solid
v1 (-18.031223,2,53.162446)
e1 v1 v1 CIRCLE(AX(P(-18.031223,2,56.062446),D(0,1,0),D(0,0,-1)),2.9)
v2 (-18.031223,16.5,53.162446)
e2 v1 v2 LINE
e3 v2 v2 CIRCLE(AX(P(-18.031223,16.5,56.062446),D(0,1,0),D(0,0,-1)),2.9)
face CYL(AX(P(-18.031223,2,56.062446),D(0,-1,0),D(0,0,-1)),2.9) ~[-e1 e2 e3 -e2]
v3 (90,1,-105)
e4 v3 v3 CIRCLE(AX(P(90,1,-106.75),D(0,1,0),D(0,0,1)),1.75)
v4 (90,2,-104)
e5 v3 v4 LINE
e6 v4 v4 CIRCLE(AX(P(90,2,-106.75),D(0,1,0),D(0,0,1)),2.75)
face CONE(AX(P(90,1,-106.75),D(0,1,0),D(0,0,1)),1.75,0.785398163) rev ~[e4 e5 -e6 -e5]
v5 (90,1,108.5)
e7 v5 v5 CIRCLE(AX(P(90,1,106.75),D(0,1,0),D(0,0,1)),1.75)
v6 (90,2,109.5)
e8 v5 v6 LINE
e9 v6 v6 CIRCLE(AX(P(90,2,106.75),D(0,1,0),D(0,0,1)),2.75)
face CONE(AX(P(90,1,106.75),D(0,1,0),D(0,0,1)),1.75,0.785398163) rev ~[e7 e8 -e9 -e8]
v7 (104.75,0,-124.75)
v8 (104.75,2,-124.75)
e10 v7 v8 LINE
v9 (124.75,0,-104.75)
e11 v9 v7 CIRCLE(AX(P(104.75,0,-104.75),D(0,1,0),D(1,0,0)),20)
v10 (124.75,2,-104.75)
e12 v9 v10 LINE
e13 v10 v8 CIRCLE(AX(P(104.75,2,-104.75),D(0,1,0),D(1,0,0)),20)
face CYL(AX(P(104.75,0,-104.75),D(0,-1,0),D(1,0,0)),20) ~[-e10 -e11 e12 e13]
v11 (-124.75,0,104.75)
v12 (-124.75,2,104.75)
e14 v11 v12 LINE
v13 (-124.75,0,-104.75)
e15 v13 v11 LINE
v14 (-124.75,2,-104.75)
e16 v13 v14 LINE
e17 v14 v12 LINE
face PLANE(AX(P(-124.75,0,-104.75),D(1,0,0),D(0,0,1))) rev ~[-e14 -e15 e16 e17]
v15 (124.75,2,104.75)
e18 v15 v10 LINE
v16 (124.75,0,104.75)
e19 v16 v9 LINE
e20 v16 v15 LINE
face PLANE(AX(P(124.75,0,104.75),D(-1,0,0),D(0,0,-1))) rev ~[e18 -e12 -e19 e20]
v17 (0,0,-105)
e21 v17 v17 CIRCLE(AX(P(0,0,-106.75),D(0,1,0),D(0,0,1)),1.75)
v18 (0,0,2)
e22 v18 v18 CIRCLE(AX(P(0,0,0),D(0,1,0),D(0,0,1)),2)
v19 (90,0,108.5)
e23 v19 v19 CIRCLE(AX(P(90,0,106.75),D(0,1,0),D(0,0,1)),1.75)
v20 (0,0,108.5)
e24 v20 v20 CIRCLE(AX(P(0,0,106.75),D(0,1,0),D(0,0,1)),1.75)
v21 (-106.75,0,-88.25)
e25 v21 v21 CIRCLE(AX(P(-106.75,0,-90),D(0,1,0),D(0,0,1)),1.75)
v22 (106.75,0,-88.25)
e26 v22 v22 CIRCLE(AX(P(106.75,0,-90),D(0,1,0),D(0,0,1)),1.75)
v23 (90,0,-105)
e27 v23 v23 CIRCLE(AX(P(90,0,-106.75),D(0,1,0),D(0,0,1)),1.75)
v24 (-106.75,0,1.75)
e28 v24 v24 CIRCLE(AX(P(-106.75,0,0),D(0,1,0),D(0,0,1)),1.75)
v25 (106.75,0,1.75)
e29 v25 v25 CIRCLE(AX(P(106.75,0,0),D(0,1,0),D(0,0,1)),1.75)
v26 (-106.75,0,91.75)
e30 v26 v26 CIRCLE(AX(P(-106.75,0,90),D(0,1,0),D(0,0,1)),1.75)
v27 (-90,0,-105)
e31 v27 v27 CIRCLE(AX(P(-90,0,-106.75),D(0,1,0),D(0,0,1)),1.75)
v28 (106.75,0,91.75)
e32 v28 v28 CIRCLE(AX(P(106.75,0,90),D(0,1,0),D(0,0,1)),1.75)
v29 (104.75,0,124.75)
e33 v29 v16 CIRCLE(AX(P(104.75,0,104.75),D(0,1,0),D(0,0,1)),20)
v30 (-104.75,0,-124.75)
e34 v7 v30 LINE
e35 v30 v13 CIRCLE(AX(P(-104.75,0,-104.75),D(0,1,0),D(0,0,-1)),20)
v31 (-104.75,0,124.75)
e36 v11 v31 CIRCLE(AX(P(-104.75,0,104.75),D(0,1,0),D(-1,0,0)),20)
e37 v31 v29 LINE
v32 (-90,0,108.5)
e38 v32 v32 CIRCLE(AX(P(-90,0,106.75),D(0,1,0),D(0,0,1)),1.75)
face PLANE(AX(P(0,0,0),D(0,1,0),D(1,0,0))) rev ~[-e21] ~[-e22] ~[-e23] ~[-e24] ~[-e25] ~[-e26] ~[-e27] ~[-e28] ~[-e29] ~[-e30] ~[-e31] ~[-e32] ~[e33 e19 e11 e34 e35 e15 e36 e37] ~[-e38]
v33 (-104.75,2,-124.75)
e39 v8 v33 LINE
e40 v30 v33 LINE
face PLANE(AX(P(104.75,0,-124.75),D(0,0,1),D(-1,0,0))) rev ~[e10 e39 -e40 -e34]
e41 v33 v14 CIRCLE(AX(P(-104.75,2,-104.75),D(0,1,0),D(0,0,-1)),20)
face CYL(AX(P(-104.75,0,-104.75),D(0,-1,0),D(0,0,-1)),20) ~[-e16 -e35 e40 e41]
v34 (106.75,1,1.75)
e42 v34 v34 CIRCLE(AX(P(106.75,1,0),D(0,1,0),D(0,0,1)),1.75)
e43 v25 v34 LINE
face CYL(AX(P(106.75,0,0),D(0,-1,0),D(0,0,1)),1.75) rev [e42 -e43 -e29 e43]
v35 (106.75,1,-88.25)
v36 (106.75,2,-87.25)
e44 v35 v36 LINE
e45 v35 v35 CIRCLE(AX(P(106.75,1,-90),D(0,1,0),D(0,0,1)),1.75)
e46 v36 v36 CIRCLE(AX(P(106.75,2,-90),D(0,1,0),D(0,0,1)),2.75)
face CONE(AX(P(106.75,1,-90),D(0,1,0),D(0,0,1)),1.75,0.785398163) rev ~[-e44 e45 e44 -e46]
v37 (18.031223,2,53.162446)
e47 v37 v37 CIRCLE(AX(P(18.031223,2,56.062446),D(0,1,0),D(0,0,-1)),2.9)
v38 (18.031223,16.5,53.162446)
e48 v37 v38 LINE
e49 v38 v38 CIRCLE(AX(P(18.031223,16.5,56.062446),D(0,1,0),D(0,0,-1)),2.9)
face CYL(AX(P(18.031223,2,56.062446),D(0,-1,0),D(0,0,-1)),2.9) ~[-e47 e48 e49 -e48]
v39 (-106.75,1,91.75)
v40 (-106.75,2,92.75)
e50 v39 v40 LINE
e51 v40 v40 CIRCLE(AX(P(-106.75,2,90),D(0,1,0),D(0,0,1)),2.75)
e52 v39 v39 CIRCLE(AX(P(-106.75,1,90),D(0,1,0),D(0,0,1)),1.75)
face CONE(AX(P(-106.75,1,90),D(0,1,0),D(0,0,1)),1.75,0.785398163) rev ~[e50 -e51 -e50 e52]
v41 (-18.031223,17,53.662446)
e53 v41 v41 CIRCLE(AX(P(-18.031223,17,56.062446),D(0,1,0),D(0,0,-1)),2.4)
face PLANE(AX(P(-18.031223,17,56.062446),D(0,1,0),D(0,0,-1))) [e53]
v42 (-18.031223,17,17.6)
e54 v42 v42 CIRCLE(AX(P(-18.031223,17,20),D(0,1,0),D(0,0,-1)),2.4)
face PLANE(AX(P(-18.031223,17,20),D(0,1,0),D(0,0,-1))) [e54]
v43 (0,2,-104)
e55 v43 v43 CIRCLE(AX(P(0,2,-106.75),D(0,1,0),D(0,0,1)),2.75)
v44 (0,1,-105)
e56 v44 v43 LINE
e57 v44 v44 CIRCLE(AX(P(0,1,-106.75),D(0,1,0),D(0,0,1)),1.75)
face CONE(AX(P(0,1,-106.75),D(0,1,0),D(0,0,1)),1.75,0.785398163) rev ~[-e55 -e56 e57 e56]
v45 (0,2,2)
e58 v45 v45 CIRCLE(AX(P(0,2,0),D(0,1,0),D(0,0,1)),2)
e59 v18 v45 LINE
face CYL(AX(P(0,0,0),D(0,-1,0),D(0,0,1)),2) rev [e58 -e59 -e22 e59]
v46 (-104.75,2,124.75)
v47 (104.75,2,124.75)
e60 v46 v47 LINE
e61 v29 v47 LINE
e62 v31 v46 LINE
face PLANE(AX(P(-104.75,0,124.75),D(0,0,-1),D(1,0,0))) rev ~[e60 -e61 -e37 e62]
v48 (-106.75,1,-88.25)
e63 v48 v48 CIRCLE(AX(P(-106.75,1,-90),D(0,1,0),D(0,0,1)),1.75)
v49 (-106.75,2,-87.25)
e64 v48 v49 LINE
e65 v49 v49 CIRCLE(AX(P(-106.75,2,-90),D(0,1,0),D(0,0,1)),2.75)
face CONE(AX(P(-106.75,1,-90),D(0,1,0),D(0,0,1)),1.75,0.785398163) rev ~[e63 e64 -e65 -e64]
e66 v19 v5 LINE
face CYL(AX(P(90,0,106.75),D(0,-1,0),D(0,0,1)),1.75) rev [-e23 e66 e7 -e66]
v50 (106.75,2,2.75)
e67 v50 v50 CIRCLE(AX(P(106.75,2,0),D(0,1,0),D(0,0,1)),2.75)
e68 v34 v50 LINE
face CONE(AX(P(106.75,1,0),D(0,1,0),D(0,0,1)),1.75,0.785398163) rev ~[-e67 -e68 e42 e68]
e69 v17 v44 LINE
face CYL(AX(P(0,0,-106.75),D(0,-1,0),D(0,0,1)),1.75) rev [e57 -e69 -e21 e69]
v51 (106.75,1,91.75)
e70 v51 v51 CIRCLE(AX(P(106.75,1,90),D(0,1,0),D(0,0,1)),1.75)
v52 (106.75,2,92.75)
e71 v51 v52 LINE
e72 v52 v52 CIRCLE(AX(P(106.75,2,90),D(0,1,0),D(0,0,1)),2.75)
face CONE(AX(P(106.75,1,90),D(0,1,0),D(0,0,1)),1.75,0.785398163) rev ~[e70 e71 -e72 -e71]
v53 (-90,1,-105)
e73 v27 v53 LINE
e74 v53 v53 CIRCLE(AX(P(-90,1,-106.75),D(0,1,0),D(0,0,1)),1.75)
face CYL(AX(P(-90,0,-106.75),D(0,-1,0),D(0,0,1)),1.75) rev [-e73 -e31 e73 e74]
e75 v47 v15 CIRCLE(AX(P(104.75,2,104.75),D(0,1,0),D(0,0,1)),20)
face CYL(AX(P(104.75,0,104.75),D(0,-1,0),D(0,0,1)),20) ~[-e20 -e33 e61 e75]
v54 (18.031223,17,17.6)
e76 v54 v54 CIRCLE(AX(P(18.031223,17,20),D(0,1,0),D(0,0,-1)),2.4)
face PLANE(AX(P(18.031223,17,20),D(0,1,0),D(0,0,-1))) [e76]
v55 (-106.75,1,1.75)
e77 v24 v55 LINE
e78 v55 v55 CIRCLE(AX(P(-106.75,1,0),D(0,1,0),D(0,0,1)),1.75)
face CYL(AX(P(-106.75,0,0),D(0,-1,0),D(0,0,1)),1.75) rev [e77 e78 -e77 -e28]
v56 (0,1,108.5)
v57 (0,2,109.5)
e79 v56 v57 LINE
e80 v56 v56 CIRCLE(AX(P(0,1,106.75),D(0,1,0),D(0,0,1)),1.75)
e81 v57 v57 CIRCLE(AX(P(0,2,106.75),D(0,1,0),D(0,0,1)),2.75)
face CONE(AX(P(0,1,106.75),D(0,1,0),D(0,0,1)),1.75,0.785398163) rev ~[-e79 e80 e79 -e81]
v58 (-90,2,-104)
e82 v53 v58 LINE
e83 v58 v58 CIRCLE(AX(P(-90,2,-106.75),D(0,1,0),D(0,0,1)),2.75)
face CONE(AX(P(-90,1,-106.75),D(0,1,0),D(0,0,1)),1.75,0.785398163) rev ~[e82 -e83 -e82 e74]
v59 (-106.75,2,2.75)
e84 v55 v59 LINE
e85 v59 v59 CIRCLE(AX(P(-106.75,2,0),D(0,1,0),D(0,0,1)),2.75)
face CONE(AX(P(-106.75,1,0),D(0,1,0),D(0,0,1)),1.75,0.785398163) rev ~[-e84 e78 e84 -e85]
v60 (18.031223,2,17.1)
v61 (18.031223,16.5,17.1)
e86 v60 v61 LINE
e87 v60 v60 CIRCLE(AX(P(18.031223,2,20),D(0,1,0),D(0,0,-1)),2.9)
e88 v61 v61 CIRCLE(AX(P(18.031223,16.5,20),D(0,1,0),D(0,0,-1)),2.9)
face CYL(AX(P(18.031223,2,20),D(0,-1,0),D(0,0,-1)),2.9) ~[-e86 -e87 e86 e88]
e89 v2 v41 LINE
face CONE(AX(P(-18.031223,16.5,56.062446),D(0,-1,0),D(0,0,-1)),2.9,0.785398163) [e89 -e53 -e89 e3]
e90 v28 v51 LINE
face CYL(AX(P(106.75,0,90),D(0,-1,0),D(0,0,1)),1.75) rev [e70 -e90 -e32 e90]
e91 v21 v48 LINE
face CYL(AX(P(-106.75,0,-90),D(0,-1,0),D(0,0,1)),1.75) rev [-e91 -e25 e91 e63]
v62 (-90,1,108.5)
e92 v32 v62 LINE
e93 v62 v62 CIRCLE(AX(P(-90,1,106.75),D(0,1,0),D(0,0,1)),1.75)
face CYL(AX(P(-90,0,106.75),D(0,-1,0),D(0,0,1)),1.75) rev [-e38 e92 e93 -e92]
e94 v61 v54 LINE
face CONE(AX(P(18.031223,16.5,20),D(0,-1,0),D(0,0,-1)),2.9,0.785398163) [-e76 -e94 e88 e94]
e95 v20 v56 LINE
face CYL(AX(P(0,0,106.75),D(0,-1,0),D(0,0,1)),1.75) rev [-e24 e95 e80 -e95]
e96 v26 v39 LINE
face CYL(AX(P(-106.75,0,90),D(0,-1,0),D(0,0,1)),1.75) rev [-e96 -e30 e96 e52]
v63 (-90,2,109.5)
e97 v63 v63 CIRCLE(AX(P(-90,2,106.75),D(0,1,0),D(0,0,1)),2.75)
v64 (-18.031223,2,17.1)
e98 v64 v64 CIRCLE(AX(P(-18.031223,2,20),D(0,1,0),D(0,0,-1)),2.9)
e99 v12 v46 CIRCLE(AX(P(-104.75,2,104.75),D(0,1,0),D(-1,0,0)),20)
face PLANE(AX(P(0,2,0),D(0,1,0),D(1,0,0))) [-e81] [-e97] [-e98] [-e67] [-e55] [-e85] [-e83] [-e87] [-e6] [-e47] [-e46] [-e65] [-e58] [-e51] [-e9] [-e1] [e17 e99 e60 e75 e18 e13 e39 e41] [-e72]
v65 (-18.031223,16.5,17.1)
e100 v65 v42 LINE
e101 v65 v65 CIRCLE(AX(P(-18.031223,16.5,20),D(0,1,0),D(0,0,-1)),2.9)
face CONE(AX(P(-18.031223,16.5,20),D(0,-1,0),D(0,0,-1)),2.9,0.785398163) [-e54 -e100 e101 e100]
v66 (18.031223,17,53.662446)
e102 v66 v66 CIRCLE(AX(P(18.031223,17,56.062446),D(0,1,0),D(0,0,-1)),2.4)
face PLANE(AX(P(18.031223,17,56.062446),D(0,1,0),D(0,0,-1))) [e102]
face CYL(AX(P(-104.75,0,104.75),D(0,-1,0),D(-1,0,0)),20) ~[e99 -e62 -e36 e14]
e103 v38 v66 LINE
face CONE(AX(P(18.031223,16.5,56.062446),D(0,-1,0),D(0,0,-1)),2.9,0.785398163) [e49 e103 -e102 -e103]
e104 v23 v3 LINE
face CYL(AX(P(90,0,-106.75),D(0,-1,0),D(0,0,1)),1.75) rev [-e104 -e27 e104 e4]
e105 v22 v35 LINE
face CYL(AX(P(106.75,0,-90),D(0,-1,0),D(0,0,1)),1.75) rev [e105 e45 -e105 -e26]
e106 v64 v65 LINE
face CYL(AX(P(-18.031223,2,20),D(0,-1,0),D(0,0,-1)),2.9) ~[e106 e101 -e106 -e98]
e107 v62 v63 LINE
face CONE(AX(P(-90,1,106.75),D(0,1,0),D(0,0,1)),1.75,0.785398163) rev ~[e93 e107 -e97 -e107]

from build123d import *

# Parameters (mm, degrees)
SKETCH1_R           = 1.75
SKETCH1_R_2         = 2
BOSS_EXTRUDE1_DEPTH = 2
CHAMFER1_SIZE       = 1
SKETCH3_R           = 2.9
BOSS_EXTRUDE2_DEPTH = 15
CHAMFER2_SIZE       = 0.5


with BuildPart() as part:
    # Sketch1 → Boss-Extrude1 (new body)
    with BuildSketch(Plane(origin=(0, 0, 0), x_dir=(1, 0, 0), z_dir=(0, 1, 0))):
        with BuildLine():
            Line((-104.75, -124.75), (104.75, -124.75))
            ThreePointArc((104.75, -124.75), (118.892135624, -118.892135624), (124.75, -104.75))
            Line((124.75, -104.75), (124.75, 104.75))
            ThreePointArc((124.75, 104.75), (118.892135624, 118.892135624), (104.75, 124.75))
            Line((104.75, 124.75), (-104.75, 124.75))
            ThreePointArc((-104.75, 124.75), (-118.892135624, 118.892135624), (-124.75, 104.75))
            Line((-124.75, 104.75), (-124.75, -104.75))
            ThreePointArc((-124.75, -104.75), (-118.892135624, -118.892135624), (-104.75, -124.75))
        make_face()
        with Locations(Location((-90, 106.75, 0), (0, 0, 270))):
            Circle(SKETCH1_R, mode=Mode.SUBTRACT)
        with Locations(Location((0, 106.75, 0), (0, 0, 270))):
            Circle(SKETCH1_R, mode=Mode.SUBTRACT)
        with Locations(Location((90, 106.75, 0), (0, 0, 270))):
            Circle(SKETCH1_R, mode=Mode.SUBTRACT)
        with Locations(Location((106.75, 90, 0), (0, 0, 270))):
            Circle(SKETCH1_R, mode=Mode.SUBTRACT)
        with Locations(Location((106.75, 0, 0), (0, 0, 270))):
            Circle(SKETCH1_R, mode=Mode.SUBTRACT)
        with Locations(Location((106.75, -90, 0), (0, 0, 270))):
            Circle(SKETCH1_R, mode=Mode.SUBTRACT)
        with Locations(Location((90, -106.75, 0), (0, 0, 270))):
            Circle(SKETCH1_R, mode=Mode.SUBTRACT)
        with Locations(Location((0, -106.75, 0), (0, 0, 270))):
            Circle(SKETCH1_R, mode=Mode.SUBTRACT)
        with Locations(Location((-90, -106.75, 0), (0, 0, 270))):
            Circle(SKETCH1_R, mode=Mode.SUBTRACT)
        with Locations(Location((-106.75, -90, 0), (0, 0, 270))):
            Circle(SKETCH1_R, mode=Mode.SUBTRACT)
        with Locations(Location((-106.75, 0, 0), (0, 0, 270))):
            Circle(SKETCH1_R, mode=Mode.SUBTRACT)
        with Locations(Location((-106.75, 90, 0), (0, 0, 270))):
            Circle(SKETCH1_R, mode=Mode.SUBTRACT)
        with Locations(Location((0, 0, 0), (0, 0, 270))):
            Circle(SKETCH1_R_2, mode=Mode.SUBTRACT)
    extrude(amount=BOSS_EXTRUDE1_DEPTH)

    # Chamfer1
    chamfer1_edges = [part.edges().sort_by_distance(p)[0] for p in [
        (-90, 2, -108.5),
        (0, 2, -108.5),
        (90, 2, -108.5),
        (106.75, 2, -91.75),
        (106.75, 2, -1.75),
        (106.75, 2, 88.25),
        (90, 2, 105),
        (0, 2, 105),
        (-90, 2, 105),
        (-106.75, 2, 88.25),
        (-106.75, 2, -1.75),
        (-106.75, 2, -91.75),
    ]]
    chamfer(chamfer1_edges, length=CHAMFER1_SIZE)

    # Sketch3 → Boss-Extrude2 (add)
    with BuildSketch(Plane(origin=(0, 2, 0), x_dir=(1, 0, 0), z_dir=(0, 1, 0))):
        with Locations(Location((-18.03122292, -20, 0), (0, 0, 90))):
            Circle(SKETCH3_R)
        with Locations(Location((18.03122292, -20, 0), (0, 0, 90))):
            Circle(SKETCH3_R)
        with Locations(Location((18.03122292, -56.062445841, 0), (0, 0, 90))):
            Circle(SKETCH3_R)
        with Locations(Location((-18.03122292, -56.062445841, 0), (0, 0, 90))):
            Circle(SKETCH3_R)
    extrude(amount=BOSS_EXTRUDE2_DEPTH)

    # Chamfer2
    chamfer2_edges = [part.edges().sort_by_distance(p)[0] for p in [
        (-18.03122292, 17, 22.9),
        (18.03122292, 17, 22.9),
        (18.03122292, 17, 58.962445841),
        (-18.03122292, 17, 58.962445841),
    ]]
    chamfer(chamfer2_edges, length=CHAMFER2_SIZE)


solid = part.part
